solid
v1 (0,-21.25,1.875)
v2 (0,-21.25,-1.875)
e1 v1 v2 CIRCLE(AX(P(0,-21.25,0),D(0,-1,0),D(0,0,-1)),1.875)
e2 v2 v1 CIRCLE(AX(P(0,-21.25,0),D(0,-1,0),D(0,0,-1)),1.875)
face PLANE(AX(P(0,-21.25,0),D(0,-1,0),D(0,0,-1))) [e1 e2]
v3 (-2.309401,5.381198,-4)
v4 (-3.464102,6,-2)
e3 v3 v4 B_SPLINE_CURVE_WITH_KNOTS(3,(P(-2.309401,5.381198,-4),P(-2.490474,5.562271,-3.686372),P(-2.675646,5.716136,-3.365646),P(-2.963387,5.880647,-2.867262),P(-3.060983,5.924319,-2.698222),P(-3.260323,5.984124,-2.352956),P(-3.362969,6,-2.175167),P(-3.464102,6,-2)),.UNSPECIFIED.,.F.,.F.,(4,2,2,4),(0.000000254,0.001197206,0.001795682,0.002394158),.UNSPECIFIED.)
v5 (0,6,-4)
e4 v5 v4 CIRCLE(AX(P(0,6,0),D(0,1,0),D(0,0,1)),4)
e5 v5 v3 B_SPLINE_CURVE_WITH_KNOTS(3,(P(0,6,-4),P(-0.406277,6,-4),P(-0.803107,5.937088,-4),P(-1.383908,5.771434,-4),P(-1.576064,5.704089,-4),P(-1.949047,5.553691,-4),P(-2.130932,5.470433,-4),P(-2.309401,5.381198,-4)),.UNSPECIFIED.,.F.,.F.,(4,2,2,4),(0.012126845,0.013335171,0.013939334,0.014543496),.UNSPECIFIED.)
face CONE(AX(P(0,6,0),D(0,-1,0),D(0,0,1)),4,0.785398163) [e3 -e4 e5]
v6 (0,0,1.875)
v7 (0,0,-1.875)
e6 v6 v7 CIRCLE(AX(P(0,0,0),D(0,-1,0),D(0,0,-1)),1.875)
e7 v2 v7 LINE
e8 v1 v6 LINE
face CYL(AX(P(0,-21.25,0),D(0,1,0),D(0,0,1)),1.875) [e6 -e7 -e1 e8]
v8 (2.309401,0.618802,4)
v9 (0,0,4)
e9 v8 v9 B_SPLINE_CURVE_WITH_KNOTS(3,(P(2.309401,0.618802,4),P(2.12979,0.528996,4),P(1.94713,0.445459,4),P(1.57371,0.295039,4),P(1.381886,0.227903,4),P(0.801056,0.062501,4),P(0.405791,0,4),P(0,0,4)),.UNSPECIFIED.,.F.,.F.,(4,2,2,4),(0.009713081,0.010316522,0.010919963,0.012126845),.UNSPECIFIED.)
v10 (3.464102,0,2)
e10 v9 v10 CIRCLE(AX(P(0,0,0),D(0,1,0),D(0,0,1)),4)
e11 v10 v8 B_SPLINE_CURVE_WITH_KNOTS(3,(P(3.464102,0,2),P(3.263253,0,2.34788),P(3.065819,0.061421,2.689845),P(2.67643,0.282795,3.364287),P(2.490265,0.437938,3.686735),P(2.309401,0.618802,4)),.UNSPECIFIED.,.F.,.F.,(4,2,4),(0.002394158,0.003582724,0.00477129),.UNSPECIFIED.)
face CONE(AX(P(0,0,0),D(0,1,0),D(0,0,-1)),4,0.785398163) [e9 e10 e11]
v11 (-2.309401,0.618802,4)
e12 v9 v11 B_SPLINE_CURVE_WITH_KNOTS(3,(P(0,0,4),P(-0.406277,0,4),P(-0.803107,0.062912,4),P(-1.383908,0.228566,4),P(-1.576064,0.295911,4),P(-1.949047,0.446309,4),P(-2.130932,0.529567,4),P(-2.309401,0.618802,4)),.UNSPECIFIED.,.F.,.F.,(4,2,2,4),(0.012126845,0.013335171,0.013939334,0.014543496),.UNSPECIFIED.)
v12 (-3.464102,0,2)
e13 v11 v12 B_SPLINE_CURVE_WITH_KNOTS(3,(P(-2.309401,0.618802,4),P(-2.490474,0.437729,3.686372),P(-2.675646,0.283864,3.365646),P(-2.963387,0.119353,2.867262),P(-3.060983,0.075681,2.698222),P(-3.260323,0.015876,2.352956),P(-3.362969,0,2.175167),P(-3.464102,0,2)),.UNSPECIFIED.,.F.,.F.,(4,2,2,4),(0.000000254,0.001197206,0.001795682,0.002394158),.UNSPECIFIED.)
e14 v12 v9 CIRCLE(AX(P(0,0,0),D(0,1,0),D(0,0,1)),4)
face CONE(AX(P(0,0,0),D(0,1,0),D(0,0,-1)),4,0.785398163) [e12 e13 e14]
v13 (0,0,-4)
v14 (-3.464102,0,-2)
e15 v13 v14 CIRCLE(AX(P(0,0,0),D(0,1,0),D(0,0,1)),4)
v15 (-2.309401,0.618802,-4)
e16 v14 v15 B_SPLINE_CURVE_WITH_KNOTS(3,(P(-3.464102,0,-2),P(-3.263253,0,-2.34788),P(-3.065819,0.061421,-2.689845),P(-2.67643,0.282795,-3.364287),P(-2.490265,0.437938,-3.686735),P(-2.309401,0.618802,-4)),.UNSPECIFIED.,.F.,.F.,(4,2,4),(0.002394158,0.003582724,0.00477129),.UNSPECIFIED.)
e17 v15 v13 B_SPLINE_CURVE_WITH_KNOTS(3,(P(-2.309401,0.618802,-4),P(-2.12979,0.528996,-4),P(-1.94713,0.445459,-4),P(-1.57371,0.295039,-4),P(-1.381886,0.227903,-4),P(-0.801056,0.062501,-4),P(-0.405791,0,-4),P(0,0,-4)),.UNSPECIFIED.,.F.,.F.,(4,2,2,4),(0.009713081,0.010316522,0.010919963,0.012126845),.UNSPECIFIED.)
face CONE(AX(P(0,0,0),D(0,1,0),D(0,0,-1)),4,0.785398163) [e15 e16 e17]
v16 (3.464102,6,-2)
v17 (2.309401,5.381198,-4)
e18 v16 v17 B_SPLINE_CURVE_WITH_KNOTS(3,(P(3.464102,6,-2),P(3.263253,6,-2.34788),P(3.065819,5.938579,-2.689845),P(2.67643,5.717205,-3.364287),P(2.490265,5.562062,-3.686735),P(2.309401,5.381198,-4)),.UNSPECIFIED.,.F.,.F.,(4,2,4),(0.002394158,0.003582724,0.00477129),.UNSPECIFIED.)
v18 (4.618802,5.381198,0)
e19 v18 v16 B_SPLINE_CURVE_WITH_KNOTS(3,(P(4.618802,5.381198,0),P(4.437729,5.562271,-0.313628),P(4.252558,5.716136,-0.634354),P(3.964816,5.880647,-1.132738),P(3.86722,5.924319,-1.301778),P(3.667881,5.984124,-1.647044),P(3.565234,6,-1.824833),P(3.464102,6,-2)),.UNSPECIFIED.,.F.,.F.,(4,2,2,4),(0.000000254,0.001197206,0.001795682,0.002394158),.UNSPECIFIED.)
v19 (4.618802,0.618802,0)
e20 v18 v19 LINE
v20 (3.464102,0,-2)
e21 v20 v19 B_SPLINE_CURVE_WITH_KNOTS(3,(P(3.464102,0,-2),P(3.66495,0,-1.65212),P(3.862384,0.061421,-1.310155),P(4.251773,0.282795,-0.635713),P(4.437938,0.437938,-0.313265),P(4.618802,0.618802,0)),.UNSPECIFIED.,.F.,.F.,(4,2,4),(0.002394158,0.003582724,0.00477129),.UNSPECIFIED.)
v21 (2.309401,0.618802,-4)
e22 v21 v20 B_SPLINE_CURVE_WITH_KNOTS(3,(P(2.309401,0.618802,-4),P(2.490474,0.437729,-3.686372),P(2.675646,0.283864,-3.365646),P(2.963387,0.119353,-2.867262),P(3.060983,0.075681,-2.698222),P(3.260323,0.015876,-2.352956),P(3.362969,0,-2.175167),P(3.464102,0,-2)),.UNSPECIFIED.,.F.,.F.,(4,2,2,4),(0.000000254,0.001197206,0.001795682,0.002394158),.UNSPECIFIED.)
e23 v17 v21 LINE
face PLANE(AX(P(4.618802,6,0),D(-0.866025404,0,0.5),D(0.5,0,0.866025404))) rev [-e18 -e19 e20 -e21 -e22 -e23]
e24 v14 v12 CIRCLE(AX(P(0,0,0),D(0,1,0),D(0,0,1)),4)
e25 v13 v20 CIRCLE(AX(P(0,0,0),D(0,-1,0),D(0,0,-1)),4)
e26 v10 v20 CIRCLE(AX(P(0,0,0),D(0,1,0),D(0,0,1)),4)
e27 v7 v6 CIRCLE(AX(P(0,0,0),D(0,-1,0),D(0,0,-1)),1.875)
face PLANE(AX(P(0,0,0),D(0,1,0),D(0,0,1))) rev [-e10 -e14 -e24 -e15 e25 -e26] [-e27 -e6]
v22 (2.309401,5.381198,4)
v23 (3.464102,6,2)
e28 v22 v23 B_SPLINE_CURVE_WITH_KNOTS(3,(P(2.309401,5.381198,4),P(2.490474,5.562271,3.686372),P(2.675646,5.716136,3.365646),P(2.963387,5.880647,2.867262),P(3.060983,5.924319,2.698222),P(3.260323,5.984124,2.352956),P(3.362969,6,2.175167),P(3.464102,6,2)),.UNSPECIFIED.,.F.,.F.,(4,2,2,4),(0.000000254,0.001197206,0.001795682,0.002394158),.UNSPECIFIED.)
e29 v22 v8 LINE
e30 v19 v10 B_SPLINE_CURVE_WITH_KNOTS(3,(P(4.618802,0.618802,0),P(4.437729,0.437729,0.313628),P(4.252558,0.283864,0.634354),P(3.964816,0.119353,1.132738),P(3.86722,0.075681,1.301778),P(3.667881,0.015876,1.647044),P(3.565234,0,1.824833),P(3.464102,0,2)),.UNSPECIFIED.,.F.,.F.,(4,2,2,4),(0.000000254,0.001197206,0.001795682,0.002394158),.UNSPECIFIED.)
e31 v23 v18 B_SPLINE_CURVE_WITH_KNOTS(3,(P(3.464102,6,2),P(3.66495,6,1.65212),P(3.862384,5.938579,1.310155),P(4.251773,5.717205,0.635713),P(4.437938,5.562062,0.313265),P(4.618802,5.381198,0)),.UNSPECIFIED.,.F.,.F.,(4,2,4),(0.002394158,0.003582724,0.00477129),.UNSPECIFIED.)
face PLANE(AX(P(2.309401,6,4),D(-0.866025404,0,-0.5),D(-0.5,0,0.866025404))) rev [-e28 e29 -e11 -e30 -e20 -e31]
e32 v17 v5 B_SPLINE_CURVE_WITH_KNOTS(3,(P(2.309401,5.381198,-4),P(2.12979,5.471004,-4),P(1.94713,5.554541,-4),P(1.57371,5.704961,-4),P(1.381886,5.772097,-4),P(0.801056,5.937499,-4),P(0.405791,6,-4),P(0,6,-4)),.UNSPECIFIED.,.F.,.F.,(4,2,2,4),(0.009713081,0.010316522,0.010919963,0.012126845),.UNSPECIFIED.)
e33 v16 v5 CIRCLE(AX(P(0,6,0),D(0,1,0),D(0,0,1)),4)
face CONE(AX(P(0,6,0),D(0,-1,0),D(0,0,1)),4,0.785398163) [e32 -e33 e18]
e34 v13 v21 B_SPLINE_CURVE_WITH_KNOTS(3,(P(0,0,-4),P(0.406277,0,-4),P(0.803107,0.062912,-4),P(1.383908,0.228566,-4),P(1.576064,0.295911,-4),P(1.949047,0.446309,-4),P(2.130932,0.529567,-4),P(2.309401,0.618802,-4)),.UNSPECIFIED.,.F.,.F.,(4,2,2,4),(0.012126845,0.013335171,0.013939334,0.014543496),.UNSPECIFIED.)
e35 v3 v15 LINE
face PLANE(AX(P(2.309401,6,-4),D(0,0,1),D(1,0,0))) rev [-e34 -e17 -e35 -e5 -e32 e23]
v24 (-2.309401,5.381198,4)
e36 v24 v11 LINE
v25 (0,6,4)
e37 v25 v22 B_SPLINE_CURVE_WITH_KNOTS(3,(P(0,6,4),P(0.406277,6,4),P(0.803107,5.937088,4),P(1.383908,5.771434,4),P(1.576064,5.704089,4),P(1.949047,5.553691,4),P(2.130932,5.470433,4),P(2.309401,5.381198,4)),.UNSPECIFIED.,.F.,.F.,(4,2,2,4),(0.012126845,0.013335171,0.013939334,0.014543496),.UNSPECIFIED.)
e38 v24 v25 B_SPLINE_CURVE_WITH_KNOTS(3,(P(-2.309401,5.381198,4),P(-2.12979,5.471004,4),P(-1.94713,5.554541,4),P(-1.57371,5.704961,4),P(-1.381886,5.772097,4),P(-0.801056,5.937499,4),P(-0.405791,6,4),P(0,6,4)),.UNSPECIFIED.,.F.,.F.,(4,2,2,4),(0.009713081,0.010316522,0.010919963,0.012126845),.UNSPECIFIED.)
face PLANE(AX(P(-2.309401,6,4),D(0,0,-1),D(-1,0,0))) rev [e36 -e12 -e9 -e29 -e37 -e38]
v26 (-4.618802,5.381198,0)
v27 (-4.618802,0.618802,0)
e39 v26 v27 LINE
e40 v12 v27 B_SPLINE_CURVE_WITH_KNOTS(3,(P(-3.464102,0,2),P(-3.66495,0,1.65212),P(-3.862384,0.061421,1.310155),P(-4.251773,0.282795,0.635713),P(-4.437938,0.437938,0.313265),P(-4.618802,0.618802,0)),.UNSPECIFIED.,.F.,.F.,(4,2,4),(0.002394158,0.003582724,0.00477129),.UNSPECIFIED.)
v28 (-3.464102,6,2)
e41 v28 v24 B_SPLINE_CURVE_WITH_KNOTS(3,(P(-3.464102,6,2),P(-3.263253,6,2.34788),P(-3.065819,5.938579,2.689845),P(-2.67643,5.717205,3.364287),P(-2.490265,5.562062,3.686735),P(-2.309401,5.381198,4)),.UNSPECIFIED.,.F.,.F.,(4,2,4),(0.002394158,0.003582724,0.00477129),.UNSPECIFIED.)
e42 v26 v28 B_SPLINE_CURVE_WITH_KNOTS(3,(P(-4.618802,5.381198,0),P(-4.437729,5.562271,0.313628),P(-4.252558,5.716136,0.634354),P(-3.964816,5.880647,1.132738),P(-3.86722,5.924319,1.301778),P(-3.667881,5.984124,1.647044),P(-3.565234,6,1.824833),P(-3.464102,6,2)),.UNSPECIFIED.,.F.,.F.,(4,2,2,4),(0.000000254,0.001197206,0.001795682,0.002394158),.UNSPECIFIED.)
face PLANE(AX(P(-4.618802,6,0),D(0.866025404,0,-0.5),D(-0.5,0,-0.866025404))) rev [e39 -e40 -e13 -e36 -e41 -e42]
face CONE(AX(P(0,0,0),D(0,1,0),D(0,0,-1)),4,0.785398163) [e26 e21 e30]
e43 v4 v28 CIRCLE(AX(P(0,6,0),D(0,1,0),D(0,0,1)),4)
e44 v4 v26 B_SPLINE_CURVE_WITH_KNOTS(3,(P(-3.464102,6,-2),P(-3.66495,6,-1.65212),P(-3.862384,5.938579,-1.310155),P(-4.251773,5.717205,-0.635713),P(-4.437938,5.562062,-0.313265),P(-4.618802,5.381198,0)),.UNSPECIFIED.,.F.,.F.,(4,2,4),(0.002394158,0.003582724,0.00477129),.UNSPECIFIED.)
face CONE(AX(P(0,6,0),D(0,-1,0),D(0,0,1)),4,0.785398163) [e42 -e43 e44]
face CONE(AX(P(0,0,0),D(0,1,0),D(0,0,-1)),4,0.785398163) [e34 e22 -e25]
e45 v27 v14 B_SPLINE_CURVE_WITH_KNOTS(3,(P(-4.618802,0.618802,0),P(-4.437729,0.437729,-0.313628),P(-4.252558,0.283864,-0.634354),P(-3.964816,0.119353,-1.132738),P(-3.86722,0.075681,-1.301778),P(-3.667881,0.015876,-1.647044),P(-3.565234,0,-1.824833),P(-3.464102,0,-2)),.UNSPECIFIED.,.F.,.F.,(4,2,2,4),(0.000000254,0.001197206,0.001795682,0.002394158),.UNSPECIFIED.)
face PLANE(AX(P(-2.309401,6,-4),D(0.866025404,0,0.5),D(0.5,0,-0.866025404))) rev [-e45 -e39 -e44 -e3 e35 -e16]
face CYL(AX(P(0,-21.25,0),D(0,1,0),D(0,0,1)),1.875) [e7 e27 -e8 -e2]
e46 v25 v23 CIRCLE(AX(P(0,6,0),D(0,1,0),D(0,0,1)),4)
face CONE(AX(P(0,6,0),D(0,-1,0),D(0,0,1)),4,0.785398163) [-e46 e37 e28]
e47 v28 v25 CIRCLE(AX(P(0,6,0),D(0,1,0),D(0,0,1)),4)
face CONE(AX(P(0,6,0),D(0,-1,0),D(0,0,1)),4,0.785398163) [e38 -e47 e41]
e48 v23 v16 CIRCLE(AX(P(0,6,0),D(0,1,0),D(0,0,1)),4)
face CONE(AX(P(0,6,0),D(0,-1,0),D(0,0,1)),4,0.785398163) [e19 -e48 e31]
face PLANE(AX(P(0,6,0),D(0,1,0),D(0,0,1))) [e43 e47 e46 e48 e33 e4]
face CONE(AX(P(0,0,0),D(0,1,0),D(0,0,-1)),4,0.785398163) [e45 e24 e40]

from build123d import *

# Parameters (mm, degrees)
HEX_HEAD_DEPTH                          = 6
HEAD_TOP_CHAMFER_SKETCH_OUTSIDE_W       = 29.96
HEAD_TOP_CHAMFER_SKETCH_OUTSIDE_H       = 28.722
HEAD_TOP_CHAMFER_SKETCH_OUTSIDE_R       = 4
HEAD_TOP_CHAMFER_45DEG_DEPTH            = 8
HEAD_TOP_CHAMFER_45DEG_DRAFT            = -45
SHANK_SKETCH_R                          = 1.875
SHANK_DEPTH                             = 21.25
HEAD_UNDERSIDE_CHAMFER_SKETCH_OUTSIDE_W = 59.71
HEAD_UNDERSIDE_CHAMFER_SKETCH_OUTSIDE_H = 58.472
HEAD_UNDERSIDE_CHAMFER_SKETCH_OUTSIDE_R = 4
HEAD_UNDERSIDE_CHAMFER_45DEG_DEPTH      = 21.25
HEAD_UNDERSIDE_CHAMFER_45DEG_DRAFT      = -45


with BuildPart() as part:
    # Hex Head Sketch → Hex Head (new body)
    with BuildSketch(Plane(origin=(0, 0, 0), x_dir=(1, 0, 0), z_dir=(0, 1, 0))):
        Polygon((-2.309401077, -4), (2.309401077, -4), (4.618802154, 0), (2.309401077, 4), (-2.309401077, 4), (-4.618802154, 0), align=None)
    extrude(amount=HEX_HEAD_DEPTH)


with BuildPart() as head_top_chamfer_45deg_tool:
    # Head Top Chamfer Sketch outside → Head Top Chamfer 45deg (with draft: the straight prism first)
    with BuildSketch(Plane(origin=(0, 6, 0), x_dir=(1, 0, 0), z_dir=(0, 1, 0))):
        Rectangle(HEAD_TOP_CHAMFER_SKETCH_OUTSIDE_W, HEAD_TOP_CHAMFER_SKETCH_OUTSIDE_H)
        Circle(HEAD_TOP_CHAMFER_SKETCH_OUTSIDE_R, mode=Mode.SUBTRACT)
    extrude(amount=-HEAD_TOP_CHAMFER_45DEG_DEPTH)
    # Head Top Chamfer 45deg: the draft: its side faces are tilted about the plane it starts from
    head_top_chamfer_45deg_sides = [head_top_chamfer_45deg_tool.faces().sort_by_distance(p)[0] for p in [
        (0, 2, 14.361),
        (14.98, 2, 0),
        (0, 2, -14.361),
        (-14.98, 2, 0),
        (-4, 2, 0),
    ]]
    draft(head_top_chamfer_45deg_sides, Plane(origin=(0, 6, 0), x_dir=(1, 0, 0), z_dir=(0, 1, 0)), HEAD_TOP_CHAMFER_45DEG_DRAFT)


with BuildPart() as part_1:
    add(part.part)

    # Head Top Chamfer 45deg: cut by head_top_chamfer_45deg_tool
    add(head_top_chamfer_45deg_tool.part, mode=Mode.SUBTRACT)

    # Shank Sketch → Shank (add)
    with BuildSketch(Plane.XZ):
        with Locations(Location((0, 0, 0), (0, 0, 270))):
            Circle(SHANK_SKETCH_R)
    extrude(amount=SHANK_DEPTH)


with BuildPart() as head_underside_chamfer_45deg_tool:
    # Head Underside Chamfer Sketch outside → Head Underside Chamfer 45deg (with draft: the straight prism first)
    with BuildSketch(Plane.XZ):
        Rectangle(HEAD_UNDERSIDE_CHAMFER_SKETCH_OUTSIDE_W, HEAD_UNDERSIDE_CHAMFER_SKETCH_OUTSIDE_H)
        Circle(HEAD_UNDERSIDE_CHAMFER_SKETCH_OUTSIDE_R, mode=Mode.SUBTRACT)
    extrude(amount=-HEAD_UNDERSIDE_CHAMFER_45DEG_DEPTH)
    # Head Underside Chamfer 45deg: the draft: its side faces are tilted about the plane it starts from
    head_underside_chamfer_45deg_sides = [head_underside_chamfer_45deg_tool.faces().sort_by_distance(p)[0] for p in [
        (0, 10.625, -29.236),
        (29.855, 10.625, 0),
        (0, 10.625, 29.236),
        (-29.855, 10.625, 0),
        (-4, 10.625, 0),
    ]]
    draft(head_underside_chamfer_45deg_sides, Plane.XZ, HEAD_UNDERSIDE_CHAMFER_45DEG_DRAFT)


with BuildPart() as part_2:
    add(part_1.part)

    # Head Underside Chamfer 45deg: cut by head_underside_chamfer_45deg_tool
    add(head_underside_chamfer_45deg_tool.part, mode=Mode.SUBTRACT)


solid = part_2.part
